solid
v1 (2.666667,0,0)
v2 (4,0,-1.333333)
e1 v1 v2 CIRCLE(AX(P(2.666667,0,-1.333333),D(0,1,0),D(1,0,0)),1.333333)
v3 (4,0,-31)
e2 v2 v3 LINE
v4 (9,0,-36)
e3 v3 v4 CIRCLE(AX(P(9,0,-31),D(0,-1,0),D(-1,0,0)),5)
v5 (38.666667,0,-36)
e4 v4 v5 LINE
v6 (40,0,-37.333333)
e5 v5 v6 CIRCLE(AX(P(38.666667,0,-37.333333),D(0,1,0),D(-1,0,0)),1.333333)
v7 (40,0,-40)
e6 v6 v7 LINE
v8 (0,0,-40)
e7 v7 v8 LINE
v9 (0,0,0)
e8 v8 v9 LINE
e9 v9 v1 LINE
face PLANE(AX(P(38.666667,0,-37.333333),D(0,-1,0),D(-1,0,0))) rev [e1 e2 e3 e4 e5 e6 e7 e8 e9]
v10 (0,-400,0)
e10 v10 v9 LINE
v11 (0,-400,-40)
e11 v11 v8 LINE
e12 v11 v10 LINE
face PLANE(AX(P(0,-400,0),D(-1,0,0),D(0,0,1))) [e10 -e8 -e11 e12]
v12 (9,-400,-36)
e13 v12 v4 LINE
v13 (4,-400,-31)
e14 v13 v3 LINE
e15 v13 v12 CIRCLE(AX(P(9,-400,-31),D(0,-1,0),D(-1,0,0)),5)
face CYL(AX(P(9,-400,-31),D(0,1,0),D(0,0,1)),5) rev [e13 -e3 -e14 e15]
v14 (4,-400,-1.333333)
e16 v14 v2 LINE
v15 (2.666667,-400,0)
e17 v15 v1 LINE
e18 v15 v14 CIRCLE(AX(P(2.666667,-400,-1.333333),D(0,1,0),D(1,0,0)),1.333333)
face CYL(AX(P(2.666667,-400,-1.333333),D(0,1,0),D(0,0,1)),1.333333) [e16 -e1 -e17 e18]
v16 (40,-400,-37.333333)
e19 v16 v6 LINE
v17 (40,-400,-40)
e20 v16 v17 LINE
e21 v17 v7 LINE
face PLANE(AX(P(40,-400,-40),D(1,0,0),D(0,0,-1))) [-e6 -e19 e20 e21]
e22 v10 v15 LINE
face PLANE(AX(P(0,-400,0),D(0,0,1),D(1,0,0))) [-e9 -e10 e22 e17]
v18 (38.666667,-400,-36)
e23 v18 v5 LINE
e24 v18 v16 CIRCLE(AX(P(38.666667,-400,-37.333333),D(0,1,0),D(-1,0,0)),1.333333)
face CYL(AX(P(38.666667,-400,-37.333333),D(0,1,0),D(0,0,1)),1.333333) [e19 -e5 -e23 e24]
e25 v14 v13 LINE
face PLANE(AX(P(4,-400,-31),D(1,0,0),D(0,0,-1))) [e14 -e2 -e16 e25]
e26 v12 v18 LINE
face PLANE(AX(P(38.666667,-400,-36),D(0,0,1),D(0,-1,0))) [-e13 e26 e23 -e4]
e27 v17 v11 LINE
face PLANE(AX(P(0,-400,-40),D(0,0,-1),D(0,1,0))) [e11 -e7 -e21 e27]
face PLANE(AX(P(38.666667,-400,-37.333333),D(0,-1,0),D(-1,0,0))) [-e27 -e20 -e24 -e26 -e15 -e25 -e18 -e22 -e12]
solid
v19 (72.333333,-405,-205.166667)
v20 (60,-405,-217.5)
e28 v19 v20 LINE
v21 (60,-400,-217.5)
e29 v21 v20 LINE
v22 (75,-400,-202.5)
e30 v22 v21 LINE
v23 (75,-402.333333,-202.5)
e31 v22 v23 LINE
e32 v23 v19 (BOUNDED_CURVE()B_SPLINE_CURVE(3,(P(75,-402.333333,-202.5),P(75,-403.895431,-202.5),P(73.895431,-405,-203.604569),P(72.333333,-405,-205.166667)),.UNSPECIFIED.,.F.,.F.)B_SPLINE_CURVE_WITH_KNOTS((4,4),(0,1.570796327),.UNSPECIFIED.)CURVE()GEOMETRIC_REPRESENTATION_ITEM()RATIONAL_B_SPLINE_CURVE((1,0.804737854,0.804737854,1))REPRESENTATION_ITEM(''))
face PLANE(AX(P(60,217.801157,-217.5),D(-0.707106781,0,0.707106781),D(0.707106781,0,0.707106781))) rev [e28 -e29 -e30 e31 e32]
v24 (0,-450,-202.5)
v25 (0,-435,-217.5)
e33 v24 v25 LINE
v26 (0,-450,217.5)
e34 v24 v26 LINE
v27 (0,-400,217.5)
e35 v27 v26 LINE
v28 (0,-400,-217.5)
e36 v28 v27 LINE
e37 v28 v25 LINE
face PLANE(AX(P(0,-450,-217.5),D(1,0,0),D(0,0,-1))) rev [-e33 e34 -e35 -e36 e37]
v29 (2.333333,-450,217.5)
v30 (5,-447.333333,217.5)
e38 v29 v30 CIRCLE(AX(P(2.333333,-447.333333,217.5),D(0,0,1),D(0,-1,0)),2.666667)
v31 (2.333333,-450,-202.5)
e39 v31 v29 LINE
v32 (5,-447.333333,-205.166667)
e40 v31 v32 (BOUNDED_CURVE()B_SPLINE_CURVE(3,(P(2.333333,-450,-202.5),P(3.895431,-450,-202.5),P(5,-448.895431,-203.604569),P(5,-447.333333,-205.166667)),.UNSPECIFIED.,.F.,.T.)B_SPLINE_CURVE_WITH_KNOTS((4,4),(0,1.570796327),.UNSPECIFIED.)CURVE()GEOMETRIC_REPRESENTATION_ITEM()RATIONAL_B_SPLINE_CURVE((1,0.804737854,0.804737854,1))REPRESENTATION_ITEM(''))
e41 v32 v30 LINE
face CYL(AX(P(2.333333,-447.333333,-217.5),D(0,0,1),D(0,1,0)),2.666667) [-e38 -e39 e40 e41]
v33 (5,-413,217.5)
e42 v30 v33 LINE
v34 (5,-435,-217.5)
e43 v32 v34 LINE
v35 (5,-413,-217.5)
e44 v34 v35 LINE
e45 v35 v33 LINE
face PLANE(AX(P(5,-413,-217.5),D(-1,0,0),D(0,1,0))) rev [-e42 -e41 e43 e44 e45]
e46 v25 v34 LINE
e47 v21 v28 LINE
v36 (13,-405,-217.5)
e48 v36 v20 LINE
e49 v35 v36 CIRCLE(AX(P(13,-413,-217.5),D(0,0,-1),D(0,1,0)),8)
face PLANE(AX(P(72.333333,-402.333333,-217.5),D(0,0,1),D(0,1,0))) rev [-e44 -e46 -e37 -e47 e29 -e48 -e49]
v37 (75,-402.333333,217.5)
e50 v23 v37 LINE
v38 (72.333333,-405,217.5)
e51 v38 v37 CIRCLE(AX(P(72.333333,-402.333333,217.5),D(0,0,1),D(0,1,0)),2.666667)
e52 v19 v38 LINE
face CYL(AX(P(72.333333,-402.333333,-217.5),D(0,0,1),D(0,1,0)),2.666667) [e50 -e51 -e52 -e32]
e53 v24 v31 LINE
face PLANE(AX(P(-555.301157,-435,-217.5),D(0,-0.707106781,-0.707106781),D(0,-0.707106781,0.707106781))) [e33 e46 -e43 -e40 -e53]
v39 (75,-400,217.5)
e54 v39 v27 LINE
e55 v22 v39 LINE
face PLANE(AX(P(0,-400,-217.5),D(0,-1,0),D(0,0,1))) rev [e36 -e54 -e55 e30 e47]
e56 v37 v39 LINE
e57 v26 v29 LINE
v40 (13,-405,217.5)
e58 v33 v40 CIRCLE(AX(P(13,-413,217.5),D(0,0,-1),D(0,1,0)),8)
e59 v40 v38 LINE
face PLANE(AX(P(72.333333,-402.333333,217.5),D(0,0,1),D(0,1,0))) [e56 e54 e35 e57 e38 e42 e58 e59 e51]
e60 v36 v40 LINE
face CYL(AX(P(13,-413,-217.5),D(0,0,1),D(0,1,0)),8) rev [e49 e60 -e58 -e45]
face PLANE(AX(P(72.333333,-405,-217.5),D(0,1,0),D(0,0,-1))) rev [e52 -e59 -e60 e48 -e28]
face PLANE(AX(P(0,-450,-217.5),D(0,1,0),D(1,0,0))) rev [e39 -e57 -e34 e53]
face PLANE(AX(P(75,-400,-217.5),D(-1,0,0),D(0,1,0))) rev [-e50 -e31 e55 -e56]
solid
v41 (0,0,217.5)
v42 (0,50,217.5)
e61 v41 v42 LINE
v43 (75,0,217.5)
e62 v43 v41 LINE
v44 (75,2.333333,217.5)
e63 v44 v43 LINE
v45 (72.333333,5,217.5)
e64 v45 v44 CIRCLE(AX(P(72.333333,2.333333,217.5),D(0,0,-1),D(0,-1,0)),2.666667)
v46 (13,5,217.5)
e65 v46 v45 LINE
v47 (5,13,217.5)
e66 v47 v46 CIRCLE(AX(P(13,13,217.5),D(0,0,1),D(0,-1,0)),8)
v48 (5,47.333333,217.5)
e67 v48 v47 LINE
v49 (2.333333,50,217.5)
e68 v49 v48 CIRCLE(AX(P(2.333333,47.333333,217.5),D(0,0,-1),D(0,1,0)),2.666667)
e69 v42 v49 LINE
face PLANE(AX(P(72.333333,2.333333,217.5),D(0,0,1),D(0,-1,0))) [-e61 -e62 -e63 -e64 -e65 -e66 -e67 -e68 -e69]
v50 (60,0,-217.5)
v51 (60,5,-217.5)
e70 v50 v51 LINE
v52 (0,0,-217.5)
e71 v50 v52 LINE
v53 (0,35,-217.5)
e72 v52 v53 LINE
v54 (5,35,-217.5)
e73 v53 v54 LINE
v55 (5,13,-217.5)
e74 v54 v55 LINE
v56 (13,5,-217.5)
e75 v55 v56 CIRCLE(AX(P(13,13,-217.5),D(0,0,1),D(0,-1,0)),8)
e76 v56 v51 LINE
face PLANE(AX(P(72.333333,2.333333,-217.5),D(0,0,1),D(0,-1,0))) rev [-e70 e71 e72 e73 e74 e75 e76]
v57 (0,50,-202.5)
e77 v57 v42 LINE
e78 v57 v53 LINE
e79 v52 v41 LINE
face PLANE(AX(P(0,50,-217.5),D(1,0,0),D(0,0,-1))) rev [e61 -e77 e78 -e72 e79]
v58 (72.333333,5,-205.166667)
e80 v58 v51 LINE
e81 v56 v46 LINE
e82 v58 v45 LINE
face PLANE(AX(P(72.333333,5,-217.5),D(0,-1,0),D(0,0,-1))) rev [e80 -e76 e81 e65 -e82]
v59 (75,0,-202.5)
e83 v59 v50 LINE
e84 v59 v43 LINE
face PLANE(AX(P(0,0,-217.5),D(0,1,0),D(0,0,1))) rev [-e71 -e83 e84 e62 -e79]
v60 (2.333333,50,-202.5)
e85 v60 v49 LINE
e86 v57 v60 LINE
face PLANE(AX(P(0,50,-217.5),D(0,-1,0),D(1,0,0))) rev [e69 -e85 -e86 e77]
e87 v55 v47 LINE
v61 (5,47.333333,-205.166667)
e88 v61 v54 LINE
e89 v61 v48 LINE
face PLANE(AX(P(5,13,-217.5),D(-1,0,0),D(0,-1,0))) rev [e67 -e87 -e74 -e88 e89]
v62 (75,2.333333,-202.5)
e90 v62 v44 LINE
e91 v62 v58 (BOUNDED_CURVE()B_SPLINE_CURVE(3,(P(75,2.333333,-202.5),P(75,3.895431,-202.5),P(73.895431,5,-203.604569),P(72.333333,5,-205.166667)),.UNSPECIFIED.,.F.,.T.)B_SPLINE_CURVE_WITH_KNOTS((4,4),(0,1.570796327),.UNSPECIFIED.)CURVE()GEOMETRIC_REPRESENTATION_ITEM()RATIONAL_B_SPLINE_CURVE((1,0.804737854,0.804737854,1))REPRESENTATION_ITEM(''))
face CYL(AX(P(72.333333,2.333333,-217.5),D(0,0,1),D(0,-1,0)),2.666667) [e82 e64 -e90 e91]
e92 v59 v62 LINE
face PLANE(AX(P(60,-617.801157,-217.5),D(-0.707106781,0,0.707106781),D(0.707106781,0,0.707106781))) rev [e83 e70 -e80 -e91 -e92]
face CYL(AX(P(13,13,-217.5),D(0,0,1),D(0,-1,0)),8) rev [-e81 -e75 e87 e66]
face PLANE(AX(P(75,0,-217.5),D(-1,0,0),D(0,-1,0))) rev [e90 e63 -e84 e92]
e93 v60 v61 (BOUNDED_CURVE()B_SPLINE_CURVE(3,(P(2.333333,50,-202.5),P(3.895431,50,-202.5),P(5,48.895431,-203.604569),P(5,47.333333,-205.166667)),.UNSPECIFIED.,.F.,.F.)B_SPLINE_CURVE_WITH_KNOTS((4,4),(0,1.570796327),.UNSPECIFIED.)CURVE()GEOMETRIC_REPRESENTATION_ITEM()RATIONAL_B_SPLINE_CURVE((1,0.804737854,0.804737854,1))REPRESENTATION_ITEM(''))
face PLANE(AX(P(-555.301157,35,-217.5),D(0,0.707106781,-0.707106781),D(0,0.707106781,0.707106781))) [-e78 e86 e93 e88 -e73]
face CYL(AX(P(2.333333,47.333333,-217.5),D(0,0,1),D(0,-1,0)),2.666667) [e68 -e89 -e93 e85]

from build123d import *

# Parameters (mm, degrees)
GBT706_2008_075_50_5_1_DEPTH = 435
CUT_EXTRUDE_1_DEPTH          = 236.438420824
CUT_EXTRUDE_1_DEPTH_BACK     = 10
CUT_EXTRUDE_2_DEPTH          = 236.438420824
CUT_EXTRUDE_2_DEPTH_BACK     = 10
GBT706_2008_040_4_1_DEPTH    = 400


with BuildPart() as part:
    # Sketch12 → Gbt706-2008 热轧不等边角钢 075×50×5(1) (new body)
    with BuildSketch(Plane.YX.offset(-217.5)):
        with BuildLine():
            Line((0, 0), (0, 75))
            Line((0, 75), (2.333333333, 75))
            ThreePointArc((2.333333333, 75), (4.218951416, 74.218951416), (5, 72.333333333))
            Line((5, 72.333333333), (5, 13))
            ThreePointArc((5, 13), (7.343145751, 7.343145751), (13, 5))
            Line((13, 5), (47.333333333, 5))
            ThreePointArc((47.333333333, 5), (49.218951416, 4.218951416), (50, 2.333333333))
            Line((50, 2.333333333), (50, 0))
            Line((50, 0), (0, 0))
        make_face()
    extrude(amount=GBT706_2008_075_50_5_1_DEPTH)

    # 草图2 → 切除-拉伸1 (cut, two sides: drawn at the far end of the back side and taken through both)
    with BuildSketch(Plane.ZY.offset(-CUT_EXTRUDE_1_DEPTH_BACK)):
        Polygon((-841.74203278, -589.24203278), (-217.5, 35), (-202.5, 50), (421.74203278, 674.24203278), (-826.74203278, 1922.726098341), (-2090.226098341, 659.24203278), align=None)
    extrude(amount=CUT_EXTRUDE_1_DEPTH + CUT_EXTRUDE_1_DEPTH_BACK, mode=Mode.SUBTRACT)

    # 草图3 → 切除-拉伸2 (cut, two sides: drawn at the far end of the back side and taken through both)
    with BuildSketch(Plane.XZ.offset(-CUT_EXTRUDE_2_DEPTH_BACK)):
        Polygon((-568.078314146, -845.578314146), (60, -217.5), (75, -202.5), (703.078314146, 425.578314146), (1959.234942439, -830.578314146), (688.078314146, -2101.734942439), align=None)
    extrude(amount=CUT_EXTRUDE_2_DEPTH + CUT_EXTRUDE_2_DEPTH_BACK, mode=Mode.SUBTRACT)


with BuildPart() as body_2:
    # 镜向2: mirrored copy
    add(part.part.mirror(Plane(origin=(0, -200, 0), x_dir=(0, 0, 1), z_dir=(0, -1, 0))))


with BuildPart() as body_3:
    # Sketch15 → Gbt706-2008 热轧等边角钢 040×4(1) (new body)
    with BuildSketch(Plane(origin=(0, 0, -40), x_dir=(0, 0, 1), z_dir=(0, 1, 0))):
        with BuildLine():
            Line((0, 0), (0, 40))
            Line((0, 40), (2.666666667, 40))
            ThreePointArc((2.666666667, 40), (3.609475708, 39.609475708), (4, 38.666666667))
            Line((4, 38.666666667), (4, 9))
            ThreePointArc((4, 9), (5.464466094, 5.464466094), (9, 4))
            Line((9, 4), (38.666666667, 4))
            ThreePointArc((38.666666667, 4), (39.609475708, 3.609475708), (40, 2.666666667))
            Line((40, 2.666666667), (40, 0))
            Line((40, 0), (0, 0))
        make_face()
    extrude(amount=-GBT706_2008_040_4_1_DEPTH)


solid = Compound([part.part, body_2.part, body_3.part])
